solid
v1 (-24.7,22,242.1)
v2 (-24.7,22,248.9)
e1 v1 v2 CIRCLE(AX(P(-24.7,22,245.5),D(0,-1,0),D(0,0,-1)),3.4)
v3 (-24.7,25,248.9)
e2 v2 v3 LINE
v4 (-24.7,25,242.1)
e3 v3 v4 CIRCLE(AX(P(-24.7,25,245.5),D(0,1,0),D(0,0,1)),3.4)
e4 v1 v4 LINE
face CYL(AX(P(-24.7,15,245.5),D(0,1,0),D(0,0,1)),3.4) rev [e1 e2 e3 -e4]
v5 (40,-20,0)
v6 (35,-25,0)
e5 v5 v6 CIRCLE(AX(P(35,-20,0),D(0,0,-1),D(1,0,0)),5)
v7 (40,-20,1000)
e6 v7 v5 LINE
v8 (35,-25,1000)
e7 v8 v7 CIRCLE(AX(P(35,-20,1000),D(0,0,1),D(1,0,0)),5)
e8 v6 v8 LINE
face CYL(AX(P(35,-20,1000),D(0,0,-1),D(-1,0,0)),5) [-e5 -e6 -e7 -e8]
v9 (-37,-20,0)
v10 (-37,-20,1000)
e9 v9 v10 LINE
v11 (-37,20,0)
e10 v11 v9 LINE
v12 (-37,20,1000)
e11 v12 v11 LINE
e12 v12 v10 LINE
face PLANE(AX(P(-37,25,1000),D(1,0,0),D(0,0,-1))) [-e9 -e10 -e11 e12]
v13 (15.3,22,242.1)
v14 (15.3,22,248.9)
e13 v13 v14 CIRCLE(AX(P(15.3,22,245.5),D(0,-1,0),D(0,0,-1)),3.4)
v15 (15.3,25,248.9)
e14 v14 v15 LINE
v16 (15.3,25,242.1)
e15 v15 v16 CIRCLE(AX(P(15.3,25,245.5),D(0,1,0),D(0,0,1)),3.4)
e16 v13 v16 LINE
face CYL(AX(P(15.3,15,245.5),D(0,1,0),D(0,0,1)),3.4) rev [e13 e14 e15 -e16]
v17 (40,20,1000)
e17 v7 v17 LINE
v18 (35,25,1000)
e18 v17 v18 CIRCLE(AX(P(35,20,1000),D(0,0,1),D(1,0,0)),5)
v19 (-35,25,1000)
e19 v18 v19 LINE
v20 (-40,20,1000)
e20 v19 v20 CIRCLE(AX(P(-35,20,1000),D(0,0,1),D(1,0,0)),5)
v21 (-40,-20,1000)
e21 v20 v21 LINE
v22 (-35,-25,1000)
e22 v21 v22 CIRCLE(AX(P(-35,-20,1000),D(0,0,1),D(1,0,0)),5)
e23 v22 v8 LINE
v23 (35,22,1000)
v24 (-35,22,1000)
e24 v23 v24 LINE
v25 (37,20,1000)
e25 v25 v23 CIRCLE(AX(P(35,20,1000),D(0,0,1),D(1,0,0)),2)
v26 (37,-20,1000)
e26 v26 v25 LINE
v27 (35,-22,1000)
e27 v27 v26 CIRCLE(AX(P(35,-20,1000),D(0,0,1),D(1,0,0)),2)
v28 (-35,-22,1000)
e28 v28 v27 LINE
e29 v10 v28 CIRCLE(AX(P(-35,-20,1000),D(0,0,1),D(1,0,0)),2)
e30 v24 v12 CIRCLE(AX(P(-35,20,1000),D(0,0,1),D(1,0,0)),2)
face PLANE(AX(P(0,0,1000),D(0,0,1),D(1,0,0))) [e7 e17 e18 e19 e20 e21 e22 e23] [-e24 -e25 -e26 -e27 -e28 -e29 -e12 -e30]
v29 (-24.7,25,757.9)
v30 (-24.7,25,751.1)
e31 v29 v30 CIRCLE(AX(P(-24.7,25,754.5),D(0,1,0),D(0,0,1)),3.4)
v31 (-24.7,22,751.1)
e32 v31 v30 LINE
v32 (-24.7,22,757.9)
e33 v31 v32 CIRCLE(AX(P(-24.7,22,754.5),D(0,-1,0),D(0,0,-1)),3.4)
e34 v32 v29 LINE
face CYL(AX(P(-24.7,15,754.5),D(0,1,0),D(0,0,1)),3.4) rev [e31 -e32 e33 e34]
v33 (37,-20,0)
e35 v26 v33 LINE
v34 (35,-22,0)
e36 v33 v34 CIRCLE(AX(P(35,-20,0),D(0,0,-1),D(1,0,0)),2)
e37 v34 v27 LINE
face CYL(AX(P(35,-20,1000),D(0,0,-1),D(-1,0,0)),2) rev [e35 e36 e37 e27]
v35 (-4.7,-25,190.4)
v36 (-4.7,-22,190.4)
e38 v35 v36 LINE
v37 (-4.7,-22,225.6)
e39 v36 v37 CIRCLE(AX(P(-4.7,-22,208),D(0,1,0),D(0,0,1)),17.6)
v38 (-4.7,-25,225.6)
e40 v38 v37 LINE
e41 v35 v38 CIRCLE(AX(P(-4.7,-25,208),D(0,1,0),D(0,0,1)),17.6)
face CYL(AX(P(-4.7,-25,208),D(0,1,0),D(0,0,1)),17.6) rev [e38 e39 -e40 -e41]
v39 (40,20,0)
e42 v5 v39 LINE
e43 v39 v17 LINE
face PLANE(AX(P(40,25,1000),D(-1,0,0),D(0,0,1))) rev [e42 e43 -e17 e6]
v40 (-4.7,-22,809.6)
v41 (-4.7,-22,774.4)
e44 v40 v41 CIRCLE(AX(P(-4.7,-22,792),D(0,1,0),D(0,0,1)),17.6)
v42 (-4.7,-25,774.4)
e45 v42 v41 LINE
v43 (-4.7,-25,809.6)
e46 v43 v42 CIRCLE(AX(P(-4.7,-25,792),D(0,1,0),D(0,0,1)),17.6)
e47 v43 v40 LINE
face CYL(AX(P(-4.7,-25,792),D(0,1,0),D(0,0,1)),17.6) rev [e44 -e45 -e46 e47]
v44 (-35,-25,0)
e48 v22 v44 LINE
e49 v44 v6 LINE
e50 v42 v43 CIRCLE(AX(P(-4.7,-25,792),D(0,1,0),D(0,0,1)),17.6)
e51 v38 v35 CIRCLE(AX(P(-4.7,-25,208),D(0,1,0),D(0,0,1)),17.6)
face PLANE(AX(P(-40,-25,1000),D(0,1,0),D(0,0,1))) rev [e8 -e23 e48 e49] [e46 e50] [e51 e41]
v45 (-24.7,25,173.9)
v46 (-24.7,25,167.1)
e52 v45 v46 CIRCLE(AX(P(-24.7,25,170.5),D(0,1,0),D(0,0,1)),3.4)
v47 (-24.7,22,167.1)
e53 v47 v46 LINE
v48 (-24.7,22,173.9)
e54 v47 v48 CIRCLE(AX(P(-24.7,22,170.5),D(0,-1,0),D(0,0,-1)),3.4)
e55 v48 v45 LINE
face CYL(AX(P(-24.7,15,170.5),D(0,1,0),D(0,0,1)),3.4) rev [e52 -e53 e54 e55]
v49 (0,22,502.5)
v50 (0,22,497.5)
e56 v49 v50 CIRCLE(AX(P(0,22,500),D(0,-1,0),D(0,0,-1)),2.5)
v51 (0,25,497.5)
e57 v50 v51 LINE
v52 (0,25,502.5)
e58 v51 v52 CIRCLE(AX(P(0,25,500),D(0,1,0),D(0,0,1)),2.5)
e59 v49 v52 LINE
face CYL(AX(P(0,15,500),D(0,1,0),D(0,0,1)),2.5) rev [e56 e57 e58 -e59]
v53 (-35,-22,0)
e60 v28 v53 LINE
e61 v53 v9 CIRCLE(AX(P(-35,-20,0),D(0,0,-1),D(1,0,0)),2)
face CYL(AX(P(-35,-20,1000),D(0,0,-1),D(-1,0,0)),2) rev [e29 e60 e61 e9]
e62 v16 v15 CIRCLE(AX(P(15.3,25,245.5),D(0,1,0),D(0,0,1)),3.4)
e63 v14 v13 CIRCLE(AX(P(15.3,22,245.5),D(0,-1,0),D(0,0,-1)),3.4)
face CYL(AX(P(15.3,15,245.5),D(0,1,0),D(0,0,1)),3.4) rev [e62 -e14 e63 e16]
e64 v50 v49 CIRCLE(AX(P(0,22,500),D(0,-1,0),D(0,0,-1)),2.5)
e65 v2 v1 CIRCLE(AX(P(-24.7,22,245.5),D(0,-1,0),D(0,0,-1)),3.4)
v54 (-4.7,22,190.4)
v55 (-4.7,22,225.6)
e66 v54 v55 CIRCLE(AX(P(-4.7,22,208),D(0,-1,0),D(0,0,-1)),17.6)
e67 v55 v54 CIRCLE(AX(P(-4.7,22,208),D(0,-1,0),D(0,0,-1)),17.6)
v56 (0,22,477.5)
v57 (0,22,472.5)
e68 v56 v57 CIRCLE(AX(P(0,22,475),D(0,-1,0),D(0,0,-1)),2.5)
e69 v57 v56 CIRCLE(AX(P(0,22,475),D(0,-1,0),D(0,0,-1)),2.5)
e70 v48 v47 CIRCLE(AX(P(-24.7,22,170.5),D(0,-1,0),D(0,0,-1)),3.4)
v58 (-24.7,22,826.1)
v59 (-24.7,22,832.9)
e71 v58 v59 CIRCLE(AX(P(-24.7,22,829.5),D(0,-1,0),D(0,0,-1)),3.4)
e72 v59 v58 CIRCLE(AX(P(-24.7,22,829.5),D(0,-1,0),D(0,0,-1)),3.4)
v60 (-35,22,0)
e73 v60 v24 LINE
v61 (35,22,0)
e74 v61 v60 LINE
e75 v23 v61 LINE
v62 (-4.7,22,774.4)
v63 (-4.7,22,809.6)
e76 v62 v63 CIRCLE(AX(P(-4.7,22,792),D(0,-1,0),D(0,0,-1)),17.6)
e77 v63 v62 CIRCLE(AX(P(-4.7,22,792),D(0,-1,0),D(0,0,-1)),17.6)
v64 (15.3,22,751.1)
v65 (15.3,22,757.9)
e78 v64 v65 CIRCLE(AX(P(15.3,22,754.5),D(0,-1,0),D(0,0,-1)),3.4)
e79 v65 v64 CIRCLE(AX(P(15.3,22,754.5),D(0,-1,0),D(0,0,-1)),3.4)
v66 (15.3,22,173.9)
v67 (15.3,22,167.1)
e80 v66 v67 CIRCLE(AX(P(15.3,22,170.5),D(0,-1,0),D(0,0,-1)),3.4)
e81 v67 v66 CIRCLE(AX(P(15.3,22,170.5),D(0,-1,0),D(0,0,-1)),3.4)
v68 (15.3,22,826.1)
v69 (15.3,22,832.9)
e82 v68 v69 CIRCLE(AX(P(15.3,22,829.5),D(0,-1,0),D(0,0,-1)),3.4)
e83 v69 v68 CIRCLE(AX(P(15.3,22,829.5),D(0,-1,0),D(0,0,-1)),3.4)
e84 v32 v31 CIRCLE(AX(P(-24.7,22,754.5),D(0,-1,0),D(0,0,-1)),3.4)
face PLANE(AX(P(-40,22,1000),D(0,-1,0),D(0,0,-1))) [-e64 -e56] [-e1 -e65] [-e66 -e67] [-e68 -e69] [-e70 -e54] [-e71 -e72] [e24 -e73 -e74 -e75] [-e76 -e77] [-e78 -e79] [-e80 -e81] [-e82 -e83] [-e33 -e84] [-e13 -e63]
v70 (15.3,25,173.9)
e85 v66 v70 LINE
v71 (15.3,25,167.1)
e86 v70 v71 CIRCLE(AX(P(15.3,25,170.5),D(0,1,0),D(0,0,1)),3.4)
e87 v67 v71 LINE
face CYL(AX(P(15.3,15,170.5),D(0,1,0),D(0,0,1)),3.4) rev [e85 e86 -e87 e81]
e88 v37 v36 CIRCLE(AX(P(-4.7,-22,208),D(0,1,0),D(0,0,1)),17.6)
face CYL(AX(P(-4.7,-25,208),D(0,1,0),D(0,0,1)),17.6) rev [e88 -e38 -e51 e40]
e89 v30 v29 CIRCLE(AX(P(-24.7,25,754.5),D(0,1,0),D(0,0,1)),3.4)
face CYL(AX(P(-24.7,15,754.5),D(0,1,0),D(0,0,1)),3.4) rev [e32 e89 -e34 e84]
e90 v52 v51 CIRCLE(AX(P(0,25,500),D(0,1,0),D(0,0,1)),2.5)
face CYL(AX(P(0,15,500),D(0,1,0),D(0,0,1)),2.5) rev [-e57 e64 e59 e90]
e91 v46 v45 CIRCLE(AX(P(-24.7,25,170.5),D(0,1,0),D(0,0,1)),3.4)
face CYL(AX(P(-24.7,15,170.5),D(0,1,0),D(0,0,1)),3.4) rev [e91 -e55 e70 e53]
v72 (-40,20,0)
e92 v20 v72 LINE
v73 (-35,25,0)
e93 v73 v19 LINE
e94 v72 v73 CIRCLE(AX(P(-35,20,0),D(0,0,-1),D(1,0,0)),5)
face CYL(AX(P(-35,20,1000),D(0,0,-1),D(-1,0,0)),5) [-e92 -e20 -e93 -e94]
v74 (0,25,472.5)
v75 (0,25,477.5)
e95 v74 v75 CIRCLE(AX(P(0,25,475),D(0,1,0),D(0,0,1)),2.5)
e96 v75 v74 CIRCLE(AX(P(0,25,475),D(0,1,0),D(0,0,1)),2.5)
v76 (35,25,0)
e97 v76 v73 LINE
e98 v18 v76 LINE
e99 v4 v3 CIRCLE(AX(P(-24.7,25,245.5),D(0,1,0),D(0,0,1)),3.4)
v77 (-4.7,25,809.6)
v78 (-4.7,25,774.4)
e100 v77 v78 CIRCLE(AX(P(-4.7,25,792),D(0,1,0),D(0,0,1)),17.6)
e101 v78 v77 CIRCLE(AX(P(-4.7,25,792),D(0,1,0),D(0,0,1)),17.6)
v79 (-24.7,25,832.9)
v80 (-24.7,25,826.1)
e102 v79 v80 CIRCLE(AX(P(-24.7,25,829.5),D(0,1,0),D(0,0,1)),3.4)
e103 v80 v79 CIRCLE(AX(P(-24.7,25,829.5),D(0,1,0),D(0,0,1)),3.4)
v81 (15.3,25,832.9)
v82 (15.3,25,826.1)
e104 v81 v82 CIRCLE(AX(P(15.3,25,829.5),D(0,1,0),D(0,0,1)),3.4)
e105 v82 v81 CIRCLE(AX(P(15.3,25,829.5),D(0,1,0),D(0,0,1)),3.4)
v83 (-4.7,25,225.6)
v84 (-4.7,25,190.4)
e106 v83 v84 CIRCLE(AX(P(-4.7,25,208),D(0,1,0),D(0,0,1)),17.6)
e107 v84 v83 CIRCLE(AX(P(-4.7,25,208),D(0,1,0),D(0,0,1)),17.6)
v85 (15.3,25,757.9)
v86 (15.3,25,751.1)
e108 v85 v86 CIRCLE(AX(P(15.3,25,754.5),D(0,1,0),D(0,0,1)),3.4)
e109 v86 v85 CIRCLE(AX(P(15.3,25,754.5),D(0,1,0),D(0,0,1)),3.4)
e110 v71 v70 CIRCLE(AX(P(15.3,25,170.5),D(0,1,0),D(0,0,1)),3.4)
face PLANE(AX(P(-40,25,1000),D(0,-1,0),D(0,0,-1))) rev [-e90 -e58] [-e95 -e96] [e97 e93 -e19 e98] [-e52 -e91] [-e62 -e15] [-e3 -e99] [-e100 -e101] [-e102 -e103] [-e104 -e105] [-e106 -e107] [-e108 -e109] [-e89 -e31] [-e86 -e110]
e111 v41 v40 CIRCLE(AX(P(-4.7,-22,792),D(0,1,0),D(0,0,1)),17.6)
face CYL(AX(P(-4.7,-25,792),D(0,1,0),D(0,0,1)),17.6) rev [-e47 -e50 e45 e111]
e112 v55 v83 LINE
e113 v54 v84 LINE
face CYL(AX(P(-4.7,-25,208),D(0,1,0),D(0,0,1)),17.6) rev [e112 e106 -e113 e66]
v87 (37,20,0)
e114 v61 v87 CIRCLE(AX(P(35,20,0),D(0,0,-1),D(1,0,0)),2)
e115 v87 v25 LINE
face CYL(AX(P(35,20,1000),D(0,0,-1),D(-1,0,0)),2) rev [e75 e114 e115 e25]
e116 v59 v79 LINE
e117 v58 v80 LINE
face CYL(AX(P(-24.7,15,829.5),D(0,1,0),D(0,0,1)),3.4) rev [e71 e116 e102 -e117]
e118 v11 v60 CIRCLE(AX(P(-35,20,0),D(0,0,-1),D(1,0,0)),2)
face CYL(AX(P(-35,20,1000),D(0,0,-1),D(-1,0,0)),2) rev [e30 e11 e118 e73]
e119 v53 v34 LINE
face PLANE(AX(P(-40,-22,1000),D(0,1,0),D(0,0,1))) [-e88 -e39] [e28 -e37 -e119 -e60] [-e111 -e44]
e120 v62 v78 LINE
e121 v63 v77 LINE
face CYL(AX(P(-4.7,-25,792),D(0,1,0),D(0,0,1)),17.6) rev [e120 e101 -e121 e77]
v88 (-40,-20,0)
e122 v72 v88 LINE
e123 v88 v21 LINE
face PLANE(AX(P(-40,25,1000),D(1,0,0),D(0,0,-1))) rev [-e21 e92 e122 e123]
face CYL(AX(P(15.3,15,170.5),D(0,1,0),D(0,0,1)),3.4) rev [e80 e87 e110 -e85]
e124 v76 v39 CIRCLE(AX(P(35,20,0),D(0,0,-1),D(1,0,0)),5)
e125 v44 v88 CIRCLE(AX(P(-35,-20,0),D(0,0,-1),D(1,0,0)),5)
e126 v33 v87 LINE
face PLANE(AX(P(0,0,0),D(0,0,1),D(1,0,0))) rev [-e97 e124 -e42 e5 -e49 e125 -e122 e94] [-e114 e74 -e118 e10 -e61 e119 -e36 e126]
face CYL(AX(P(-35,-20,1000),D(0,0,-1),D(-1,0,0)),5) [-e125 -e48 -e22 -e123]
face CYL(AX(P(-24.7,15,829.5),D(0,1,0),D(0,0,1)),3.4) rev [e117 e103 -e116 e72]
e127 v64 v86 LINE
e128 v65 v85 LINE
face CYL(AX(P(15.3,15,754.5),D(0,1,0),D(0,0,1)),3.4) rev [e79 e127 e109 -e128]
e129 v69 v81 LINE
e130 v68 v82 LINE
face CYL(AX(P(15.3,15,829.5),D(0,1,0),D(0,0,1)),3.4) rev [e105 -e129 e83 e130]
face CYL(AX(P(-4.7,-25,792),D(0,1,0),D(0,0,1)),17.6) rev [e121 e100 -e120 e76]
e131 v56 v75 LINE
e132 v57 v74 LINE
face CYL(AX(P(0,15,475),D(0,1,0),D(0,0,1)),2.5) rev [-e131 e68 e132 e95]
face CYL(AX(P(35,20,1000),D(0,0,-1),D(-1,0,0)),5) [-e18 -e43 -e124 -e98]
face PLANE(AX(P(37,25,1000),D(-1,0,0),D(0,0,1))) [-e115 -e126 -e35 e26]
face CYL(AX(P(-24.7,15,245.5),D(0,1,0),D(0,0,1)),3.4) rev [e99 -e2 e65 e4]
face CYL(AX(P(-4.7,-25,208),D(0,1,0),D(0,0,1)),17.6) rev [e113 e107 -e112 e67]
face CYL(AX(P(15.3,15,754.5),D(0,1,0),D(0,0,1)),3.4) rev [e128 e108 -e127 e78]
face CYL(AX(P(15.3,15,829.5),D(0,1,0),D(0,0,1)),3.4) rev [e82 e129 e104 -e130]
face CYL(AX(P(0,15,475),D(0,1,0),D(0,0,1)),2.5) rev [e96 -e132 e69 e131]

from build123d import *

# Parameters (mm, degrees)
SKETCH_1_W          = 80
SKETCH_1_H          = 50
EXTRUDE_1_DEPTH     = 1000
FILLET_1_R          = 5
SHELL_1_T           = -3
SKETCH_2_R          = 17.6
CUT_EXTRUDE_1_DEPTH = 1003.047903047
SKETCH_3_R          = 3.4
CUT_EXTRUDE_2_DEPTH = 10
SKETCH_4_R          = 2.5
CUT_EXTRUDE_3_DEPTH = 10


with BuildPart() as part:
    # 草图1 → 凸台-拉伸1 (new body)
    with BuildSketch(Plane.XY):
        Rectangle(SKETCH_1_W, SKETCH_1_H)
    extrude(amount=EXTRUDE_1_DEPTH)

    # 圆角1
    fillet_1_edges = [part.edges().sort_by_distance(p)[0] for p in [
        (40, -25, 500),
        (-40, -25, 500),
        (-40, 25, 500),
        (40, 25, 500),
    ]]
    fillet(fillet_1_edges, radius=FILLET_1_R)

    # 抽壳1
    shell_1_openings = [part.faces().sort_by_distance(p)[0] for p in [
        (0, 0, 1000),
        (0, 0, 0),
    ]]
    offset(amount=SHELL_1_T, openings=shell_1_openings, kind=Kind.INTERSECTION)

    # 草图2 → 切除-拉伸1 (cut, through all)
    with BuildSketch(Plane(origin=(0, 25, 0), x_dir=(1, 0, 0), z_dir=(0, 1, 0))):
        with Locations(Location((-4.7, -208, 0), (0, 0, 270))):
            Circle(SKETCH_2_R)
        with Locations(Location((-4.7, -792, 0), (0, 0, 270))):
            Circle(SKETCH_2_R)
    extrude(amount=-CUT_EXTRUDE_1_DEPTH, mode=Mode.SUBTRACT)

    # 草图3 → 切除-拉伸2 (cut)
    with BuildSketch(Plane(origin=(0, 25, 0), x_dir=(1, 0, 0), z_dir=(0, 1, 0))):
        with Locations(Location((15.3, -170.5, 0), (0, 0, 270))):
            Circle(SKETCH_3_R)
        with Locations(Location((-24.7, -170.5, 0), (0, 0, 270))):
            Circle(SKETCH_3_R)
        with Locations(Location((-24.7, -245.5, 0), (0, 0, 270))):
            Circle(SKETCH_3_R)
        with Locations(Location((15.3, -245.5, 0), (0, 0, 270))):
            Circle(SKETCH_3_R)
        with Locations(Location((15.3, -754.5, 0), (0, 0, 270))):
            Circle(SKETCH_3_R)
        with Locations(Location((-24.7, -754.5, 0), (0, 0, 270))):
            Circle(SKETCH_3_R)
        with Locations(Location((-24.7, -829.5, 0), (0, 0, 270))):
            Circle(SKETCH_3_R)
        with Locations(Location((15.3, -829.5, 0), (0, 0, 270))):
            Circle(SKETCH_3_R)
    extrude(amount=-CUT_EXTRUDE_2_DEPTH, mode=Mode.SUBTRACT)

    # 草图4 → 切除-拉伸3 (cut)
    with BuildSketch(Plane(origin=(0, 25, 0), x_dir=(1, 0, 0), z_dir=(0, 1, 0))):
        with Locations(Location((0, -475, 0), (0, 0, 270))):
            Circle(SKETCH_4_R)
        with Locations(Location((0, -500, 0), (0, 0, 270))):
            Circle(SKETCH_4_R)
    extrude(amount=-CUT_EXTRUDE_3_DEPTH, mode=Mode.SUBTRACT)


solid = part.part
